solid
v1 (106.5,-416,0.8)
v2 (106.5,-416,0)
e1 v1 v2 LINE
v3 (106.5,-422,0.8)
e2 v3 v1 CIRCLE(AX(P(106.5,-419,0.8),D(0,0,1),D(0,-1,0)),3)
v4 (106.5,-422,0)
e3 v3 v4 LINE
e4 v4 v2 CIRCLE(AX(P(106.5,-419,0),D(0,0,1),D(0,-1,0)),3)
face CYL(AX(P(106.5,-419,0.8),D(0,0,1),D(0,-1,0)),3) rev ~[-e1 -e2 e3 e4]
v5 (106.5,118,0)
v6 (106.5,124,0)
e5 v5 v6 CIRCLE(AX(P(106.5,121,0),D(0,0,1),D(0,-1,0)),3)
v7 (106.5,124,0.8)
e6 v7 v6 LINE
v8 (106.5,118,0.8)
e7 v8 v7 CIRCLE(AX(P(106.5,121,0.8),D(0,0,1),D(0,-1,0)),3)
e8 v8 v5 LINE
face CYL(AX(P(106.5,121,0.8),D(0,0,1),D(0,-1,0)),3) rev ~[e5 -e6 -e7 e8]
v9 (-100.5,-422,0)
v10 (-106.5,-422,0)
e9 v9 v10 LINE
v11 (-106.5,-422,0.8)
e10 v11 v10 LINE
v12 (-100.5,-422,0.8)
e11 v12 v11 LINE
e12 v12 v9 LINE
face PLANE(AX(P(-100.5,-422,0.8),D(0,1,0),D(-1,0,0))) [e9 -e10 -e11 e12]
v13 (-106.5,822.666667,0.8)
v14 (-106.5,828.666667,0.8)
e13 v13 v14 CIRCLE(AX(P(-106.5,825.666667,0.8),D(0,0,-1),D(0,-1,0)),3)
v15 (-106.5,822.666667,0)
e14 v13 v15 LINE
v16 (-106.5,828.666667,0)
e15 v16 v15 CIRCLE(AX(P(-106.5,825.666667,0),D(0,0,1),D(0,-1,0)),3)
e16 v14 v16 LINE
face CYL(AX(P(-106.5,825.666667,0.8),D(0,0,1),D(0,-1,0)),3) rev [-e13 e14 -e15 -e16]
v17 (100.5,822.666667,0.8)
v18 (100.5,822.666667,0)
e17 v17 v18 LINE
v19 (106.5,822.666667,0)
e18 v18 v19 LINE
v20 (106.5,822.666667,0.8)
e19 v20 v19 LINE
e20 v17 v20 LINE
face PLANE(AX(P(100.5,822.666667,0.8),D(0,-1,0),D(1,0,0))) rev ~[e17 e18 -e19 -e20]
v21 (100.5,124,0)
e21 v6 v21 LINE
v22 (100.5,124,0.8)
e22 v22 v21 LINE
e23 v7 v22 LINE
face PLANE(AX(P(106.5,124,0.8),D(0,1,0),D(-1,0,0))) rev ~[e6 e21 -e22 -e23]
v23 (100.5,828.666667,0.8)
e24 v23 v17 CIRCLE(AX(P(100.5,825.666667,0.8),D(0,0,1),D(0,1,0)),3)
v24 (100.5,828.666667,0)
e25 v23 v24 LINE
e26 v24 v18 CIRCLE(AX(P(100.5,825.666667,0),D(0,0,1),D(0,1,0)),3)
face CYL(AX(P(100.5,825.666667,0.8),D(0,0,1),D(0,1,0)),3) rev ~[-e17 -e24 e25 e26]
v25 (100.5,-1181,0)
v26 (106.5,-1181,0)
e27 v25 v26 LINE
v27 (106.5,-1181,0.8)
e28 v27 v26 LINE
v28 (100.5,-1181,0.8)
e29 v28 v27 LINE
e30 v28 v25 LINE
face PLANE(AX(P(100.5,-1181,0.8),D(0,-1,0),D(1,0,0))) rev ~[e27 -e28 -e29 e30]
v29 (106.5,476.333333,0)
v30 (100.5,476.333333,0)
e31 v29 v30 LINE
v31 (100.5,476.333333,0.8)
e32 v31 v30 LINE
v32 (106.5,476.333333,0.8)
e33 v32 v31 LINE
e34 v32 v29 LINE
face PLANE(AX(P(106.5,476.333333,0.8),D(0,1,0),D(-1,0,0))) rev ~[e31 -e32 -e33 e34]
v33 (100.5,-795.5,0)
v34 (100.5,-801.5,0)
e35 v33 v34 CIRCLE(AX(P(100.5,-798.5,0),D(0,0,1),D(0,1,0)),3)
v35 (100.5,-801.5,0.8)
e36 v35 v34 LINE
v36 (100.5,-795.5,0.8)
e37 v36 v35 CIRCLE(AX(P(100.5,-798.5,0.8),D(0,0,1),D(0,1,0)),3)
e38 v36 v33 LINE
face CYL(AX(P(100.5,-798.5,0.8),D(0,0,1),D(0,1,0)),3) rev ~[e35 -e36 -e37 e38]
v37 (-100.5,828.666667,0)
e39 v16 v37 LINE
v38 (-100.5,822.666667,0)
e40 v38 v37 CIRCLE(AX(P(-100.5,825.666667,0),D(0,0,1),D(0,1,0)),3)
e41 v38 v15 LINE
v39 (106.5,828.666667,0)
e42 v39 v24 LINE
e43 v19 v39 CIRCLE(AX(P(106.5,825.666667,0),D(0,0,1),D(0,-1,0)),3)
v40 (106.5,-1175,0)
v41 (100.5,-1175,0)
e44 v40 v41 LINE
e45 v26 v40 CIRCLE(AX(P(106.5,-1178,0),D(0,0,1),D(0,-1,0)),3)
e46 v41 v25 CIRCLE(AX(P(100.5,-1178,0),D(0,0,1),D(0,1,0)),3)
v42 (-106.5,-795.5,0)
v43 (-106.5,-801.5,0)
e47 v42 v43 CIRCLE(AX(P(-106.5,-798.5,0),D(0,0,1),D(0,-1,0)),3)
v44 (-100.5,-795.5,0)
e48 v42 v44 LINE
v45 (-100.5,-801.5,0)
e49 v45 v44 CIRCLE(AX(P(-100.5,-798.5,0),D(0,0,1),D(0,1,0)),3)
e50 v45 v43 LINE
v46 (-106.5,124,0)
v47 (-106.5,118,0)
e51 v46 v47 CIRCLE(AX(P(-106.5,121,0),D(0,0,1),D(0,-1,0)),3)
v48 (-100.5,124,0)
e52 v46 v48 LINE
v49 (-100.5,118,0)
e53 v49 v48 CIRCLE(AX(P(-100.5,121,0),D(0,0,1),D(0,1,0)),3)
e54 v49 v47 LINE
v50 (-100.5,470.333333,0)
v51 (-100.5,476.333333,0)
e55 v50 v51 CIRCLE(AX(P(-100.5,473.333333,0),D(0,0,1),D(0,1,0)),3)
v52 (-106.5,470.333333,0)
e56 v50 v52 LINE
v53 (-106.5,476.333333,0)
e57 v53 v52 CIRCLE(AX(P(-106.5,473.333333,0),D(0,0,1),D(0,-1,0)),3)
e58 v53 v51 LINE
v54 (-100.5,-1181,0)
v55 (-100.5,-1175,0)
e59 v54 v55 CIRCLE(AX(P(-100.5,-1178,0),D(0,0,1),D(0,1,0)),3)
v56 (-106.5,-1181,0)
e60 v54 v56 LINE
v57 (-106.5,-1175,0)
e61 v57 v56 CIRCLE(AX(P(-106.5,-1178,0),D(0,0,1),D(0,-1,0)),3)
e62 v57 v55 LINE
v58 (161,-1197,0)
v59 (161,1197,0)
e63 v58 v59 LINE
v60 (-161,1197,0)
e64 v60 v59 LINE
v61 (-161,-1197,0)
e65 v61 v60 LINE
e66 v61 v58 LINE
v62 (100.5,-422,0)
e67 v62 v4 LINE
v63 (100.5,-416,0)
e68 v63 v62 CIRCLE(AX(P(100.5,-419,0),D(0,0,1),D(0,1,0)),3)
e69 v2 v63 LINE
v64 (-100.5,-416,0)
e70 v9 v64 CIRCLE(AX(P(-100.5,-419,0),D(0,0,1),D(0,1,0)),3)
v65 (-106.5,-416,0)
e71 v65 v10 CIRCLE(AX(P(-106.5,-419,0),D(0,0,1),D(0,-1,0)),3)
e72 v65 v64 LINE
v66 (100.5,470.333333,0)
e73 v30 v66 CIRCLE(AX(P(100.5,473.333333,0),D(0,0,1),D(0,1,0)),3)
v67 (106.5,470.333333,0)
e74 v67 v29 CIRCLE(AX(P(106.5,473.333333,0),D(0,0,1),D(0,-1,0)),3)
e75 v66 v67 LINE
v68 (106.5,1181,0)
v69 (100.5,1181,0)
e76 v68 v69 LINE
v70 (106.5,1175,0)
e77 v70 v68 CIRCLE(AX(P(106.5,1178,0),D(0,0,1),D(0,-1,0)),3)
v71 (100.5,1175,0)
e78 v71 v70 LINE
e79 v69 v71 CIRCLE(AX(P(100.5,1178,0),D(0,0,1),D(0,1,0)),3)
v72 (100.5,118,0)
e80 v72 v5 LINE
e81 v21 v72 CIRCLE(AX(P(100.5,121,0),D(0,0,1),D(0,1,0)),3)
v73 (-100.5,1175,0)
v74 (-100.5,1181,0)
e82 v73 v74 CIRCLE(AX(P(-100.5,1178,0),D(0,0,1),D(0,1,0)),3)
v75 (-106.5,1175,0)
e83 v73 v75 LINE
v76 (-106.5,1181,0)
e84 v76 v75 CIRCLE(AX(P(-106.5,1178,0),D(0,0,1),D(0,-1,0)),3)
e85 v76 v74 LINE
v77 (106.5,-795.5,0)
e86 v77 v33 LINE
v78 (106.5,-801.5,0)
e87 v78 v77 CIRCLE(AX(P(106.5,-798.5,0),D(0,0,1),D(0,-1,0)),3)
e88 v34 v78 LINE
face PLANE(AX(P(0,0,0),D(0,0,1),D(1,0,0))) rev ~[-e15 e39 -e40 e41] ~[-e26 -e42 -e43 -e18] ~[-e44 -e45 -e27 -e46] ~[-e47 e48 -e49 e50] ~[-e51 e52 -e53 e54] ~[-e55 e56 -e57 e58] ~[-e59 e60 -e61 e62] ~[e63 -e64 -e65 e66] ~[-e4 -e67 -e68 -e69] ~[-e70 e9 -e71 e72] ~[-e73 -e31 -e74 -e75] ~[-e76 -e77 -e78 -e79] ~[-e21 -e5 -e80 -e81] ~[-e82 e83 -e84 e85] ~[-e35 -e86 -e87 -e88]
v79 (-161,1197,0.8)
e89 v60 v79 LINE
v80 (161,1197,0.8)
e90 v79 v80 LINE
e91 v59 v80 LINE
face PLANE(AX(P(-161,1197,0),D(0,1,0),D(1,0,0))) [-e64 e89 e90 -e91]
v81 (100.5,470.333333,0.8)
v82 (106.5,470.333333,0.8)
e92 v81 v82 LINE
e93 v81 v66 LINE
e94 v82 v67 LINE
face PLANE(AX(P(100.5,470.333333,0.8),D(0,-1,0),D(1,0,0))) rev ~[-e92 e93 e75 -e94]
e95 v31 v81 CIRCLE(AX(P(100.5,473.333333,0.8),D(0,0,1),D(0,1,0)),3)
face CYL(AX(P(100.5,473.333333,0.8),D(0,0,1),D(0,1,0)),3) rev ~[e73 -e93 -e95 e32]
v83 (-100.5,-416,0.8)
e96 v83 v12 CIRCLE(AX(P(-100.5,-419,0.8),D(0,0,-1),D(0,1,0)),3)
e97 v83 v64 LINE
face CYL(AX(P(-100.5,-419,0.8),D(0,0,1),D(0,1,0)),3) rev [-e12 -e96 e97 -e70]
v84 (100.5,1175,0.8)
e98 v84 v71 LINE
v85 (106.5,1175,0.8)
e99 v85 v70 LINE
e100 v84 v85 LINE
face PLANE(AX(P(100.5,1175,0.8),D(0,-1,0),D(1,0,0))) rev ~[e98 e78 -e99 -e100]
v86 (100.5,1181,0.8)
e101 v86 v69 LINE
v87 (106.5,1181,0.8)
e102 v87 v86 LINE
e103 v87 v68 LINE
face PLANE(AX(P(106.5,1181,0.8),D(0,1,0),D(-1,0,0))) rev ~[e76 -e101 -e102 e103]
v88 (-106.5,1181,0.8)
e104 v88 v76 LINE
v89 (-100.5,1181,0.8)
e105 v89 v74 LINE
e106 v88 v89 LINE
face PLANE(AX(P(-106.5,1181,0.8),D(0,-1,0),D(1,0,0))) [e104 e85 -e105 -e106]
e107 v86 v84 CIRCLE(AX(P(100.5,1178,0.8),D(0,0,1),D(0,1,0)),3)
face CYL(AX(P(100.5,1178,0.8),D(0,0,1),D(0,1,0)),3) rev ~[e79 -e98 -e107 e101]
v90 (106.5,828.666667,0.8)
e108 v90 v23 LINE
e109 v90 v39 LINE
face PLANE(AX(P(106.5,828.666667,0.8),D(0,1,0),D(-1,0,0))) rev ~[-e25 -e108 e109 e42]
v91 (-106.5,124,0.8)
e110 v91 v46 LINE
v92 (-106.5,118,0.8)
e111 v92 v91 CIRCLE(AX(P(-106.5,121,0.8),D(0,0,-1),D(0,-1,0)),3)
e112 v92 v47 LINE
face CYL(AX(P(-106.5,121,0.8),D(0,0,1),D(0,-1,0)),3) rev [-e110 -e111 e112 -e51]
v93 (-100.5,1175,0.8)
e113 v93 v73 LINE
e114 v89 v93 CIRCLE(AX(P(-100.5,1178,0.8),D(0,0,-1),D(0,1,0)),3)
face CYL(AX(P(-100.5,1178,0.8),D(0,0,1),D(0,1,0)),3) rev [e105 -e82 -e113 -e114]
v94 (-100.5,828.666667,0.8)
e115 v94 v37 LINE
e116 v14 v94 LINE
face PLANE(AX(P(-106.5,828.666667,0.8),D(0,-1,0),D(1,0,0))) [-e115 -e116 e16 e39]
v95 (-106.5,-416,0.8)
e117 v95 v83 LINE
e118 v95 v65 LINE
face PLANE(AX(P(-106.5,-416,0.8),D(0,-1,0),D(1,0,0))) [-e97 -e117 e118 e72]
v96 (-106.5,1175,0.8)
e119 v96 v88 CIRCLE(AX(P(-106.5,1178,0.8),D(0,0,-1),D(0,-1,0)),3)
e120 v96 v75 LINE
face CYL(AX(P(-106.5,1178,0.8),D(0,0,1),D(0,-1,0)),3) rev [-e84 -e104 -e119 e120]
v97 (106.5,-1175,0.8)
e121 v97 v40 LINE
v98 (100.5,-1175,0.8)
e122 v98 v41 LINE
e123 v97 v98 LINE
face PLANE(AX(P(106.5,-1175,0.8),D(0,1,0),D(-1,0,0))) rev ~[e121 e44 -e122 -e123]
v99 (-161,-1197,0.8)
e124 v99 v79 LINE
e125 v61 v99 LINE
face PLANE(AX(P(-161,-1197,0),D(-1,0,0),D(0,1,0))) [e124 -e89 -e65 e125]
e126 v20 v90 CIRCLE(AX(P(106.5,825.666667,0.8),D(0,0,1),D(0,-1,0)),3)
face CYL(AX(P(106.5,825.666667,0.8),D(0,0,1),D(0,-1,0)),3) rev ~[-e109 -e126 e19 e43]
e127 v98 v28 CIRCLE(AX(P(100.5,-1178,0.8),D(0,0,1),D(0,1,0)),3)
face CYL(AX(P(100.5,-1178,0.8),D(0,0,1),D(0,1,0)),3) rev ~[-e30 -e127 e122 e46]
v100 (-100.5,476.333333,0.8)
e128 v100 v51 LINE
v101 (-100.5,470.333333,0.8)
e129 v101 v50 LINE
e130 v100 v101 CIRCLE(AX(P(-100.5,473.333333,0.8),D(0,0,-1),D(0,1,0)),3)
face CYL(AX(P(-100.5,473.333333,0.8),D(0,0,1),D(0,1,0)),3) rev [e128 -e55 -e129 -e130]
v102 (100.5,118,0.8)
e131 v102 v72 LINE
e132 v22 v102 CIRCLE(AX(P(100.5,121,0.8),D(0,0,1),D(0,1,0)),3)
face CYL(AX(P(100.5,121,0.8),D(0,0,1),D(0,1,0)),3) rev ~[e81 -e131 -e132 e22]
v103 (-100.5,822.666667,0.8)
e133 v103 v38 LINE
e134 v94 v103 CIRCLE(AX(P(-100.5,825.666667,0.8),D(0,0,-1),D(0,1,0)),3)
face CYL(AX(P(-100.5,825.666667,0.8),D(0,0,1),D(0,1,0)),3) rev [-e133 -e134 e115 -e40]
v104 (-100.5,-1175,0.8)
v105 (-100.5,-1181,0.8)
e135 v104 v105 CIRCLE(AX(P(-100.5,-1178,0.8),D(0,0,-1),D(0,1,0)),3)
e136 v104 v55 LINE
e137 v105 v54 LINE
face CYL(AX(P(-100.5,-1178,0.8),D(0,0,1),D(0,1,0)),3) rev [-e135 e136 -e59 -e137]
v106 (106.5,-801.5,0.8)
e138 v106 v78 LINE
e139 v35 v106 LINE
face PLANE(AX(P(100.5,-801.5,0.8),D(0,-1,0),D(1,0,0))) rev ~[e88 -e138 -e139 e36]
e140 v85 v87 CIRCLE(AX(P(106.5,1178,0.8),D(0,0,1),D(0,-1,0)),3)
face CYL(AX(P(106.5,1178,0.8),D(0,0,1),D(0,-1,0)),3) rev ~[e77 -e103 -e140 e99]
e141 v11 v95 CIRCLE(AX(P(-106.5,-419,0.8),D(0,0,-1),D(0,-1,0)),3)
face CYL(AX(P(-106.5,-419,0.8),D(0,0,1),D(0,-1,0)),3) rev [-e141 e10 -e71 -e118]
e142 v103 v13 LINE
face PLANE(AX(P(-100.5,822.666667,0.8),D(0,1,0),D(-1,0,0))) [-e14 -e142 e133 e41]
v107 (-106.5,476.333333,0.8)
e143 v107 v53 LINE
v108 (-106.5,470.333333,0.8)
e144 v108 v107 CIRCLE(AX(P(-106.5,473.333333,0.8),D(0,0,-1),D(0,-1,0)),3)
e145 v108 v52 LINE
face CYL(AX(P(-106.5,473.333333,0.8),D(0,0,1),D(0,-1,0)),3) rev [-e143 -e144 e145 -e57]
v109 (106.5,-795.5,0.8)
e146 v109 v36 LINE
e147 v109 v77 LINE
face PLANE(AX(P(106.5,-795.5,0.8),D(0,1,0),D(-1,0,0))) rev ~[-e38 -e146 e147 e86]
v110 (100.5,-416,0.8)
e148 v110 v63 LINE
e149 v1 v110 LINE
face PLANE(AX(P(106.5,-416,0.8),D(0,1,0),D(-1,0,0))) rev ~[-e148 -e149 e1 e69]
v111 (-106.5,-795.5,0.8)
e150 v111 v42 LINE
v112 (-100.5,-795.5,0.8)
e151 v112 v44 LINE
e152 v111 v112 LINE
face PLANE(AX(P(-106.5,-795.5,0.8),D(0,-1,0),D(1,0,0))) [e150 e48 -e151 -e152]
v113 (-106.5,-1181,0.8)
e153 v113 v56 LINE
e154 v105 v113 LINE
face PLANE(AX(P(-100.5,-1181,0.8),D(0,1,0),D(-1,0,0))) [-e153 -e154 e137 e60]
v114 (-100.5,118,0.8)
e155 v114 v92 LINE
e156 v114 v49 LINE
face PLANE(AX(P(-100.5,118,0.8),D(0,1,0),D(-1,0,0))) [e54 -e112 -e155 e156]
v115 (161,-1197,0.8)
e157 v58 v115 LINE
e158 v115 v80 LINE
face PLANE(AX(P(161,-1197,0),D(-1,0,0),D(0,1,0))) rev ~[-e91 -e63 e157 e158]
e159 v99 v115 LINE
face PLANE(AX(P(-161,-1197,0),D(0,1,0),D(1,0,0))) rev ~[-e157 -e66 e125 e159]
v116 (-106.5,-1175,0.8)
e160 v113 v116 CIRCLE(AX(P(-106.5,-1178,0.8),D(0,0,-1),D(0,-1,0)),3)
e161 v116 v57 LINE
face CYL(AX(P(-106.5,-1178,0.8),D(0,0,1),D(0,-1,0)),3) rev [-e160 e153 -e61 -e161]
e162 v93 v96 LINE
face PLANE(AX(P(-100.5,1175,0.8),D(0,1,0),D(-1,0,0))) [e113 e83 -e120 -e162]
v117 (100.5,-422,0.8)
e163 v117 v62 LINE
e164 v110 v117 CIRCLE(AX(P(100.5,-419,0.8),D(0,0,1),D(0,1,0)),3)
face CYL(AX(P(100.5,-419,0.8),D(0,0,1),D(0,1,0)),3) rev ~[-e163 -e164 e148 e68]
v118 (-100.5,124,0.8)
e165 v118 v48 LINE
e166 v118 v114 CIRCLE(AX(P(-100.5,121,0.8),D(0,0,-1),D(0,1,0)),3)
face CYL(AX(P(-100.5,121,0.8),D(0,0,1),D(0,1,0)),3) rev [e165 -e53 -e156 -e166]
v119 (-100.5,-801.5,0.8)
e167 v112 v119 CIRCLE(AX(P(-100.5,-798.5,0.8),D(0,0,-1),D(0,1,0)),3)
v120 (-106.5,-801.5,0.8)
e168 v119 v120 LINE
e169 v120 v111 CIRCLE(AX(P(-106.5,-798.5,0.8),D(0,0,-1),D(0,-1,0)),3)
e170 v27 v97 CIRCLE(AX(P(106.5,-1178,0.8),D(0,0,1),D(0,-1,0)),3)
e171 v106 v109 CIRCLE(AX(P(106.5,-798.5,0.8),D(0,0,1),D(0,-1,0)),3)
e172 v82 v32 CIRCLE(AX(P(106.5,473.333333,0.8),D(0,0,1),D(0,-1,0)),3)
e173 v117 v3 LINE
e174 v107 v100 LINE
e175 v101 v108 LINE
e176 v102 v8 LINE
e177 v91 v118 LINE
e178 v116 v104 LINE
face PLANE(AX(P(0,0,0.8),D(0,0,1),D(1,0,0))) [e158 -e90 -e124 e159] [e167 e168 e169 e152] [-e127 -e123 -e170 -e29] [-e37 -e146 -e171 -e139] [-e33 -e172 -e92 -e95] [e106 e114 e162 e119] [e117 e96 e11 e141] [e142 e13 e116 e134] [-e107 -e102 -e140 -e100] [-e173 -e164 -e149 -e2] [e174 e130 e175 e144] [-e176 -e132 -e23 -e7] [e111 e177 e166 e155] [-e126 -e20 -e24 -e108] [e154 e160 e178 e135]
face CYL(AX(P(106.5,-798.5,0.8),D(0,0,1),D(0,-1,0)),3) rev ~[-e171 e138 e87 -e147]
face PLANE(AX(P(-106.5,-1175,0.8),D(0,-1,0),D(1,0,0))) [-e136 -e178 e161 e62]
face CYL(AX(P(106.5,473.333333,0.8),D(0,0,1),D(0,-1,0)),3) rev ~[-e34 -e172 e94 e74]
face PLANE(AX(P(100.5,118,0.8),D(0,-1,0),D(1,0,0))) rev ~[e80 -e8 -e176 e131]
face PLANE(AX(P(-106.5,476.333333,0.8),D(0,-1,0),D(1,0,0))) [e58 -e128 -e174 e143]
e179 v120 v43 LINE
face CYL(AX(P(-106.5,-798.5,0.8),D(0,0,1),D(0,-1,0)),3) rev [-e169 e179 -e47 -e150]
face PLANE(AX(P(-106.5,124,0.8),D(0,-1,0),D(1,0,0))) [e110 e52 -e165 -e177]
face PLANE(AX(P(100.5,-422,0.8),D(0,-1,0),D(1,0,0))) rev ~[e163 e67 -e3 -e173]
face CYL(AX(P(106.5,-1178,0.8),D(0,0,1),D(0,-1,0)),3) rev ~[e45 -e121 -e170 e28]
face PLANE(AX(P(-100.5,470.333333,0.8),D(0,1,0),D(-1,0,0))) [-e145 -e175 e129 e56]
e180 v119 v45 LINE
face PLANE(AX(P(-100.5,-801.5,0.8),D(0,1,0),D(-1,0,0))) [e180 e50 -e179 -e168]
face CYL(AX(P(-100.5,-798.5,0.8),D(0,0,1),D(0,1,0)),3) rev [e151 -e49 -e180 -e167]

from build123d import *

# Parameters (mm, degrees)
SKETCH_1_W             = 322
SKETCH_1_H             = 2394
EXTRUDE_1_DEPTH        = 0.8
CUT_EXTRUDE_3001_DEPTH = 10


with BuildPart() as part:
    # 草图1 → 凸台-拉伸1 (new body)
    with BuildSketch(Plane.XY):
        Rectangle(SKETCH_1_W, SKETCH_1_H)
    extrude(amount=EXTRUDE_1_DEPTH)

    # 草图2 → 3001 (cut)
    with BuildSketch(Plane.XY.offset(0.8)):
        with BuildLine():
            Line((-106.5, 124), (-100.5, 124))
            ThreePointArc((-100.5, 124), (-97.5, 121), (-100.5, 118))
            Line((-100.5, 118), (-106.5, 118))
            ThreePointArc((-106.5, 118), (-109.5, 121), (-106.5, 124))
        make_face()
        with BuildLine():
            Line((-106.5, 1181), (-100.5, 1181))
            ThreePointArc((-100.5, 1181), (-97.5, 1178), (-100.5, 1175))
            Line((-100.5, 1175), (-106.5, 1175))
            ThreePointArc((-106.5, 1175), (-109.5, 1178), (-106.5, 1181))
        make_face()
        with BuildLine():
            Line((-106.5, 828.666666667), (-100.5, 828.666666667))
            ThreePointArc((-100.5, 828.666666667), (-97.5, 825.666666667), (-100.5, 822.666666667))
            Line((-100.5, 822.666666667), (-106.5, 822.666666667))
            ThreePointArc((-106.5, 822.666666667), (-109.5, 825.666666667), (-106.5, 828.666666667))
        make_face()
        with BuildLine():
            Line((-106.5, -1175), (-100.5, -1175))
            ThreePointArc((-100.5, -1175), (-97.5, -1178), (-100.5, -1181))
            Line((-100.5, -1181), (-106.5, -1181))
            ThreePointArc((-106.5, -1181), (-109.5, -1178), (-106.5, -1175))
        make_face()
        with BuildLine():
            Line((-106.5, 476.333333333), (-100.5, 476.333333333))
            ThreePointArc((-100.5, 476.333333333), (-97.5, 473.333333333), (-100.5, 470.333333333))
            Line((-100.5, 470.333333333), (-106.5, 470.333333333))
            ThreePointArc((-106.5, 470.333333333), (-109.5, 473.333333333), (-106.5, 476.333333333))
        make_face()
        with BuildLine():
            Line((-106.5, -795.5), (-100.5, -795.5))
            ThreePointArc((-100.5, -795.5), (-97.5, -798.5), (-100.5, -801.5))
            Line((-100.5, -801.5), (-106.5, -801.5))
            ThreePointArc((-106.5, -801.5), (-109.5, -798.5), (-106.5, -795.5))
        make_face()
        with BuildLine():
            Line((-106.5, -416), (-100.5, -416))
            ThreePointArc((-100.5, -416), (-97.5, -419), (-100.5, -422))
            Line((-100.5, -422), (-106.5, -422))
            ThreePointArc((-106.5, -422), (-109.5, -419), (-106.5, -416))
        make_face()
        with BuildLine():
            Line((106.5, -1175), (100.5, -1175))
            ThreePointArc((100.5, -1175), (97.5, -1178), (100.5, -1181))
            Line((100.5, -1181), (106.5, -1181))
            ThreePointArc((106.5, -1181), (109.5, -1178), (106.5, -1175))
        make_face()
        with BuildLine():
            Line((106.5, -795.5), (100.5, -795.5))
            ThreePointArc((100.5, -795.5), (97.5, -798.5), (100.5, -801.5))
            Line((100.5, -801.5), (106.5, -801.5))
            ThreePointArc((106.5, -801.5), (109.5, -798.5), (106.5, -795.5))
        make_face()
        with BuildLine():
            Line((106.5, -416), (100.5, -416))
            ThreePointArc((100.5, -416), (97.5, -419), (100.5, -422))
            Line((100.5, -422), (106.5, -422))
            ThreePointArc((106.5, -422), (109.5, -419), (106.5, -416))
        make_face()
        with BuildLine():
            Line((106.5, 476.333333333), (100.5, 476.333333333))
            ThreePointArc((100.5, 476.333333333), (97.5, 473.333333333), (100.5, 470.333333333))
            Line((100.5, 470.333333333), (106.5, 470.333333333))
            ThreePointArc((106.5, 470.333333333), (109.5, 473.333333333), (106.5, 476.333333333))
        make_face()
        with BuildLine():
            Line((106.5, 828.666666667), (100.5, 828.666666667))
            ThreePointArc((100.5, 828.666666667), (97.5, 825.666666667), (100.5, 822.666666667))
            Line((100.5, 822.666666667), (106.5, 822.666666667))
            ThreePointArc((106.5, 822.666666667), (109.5, 825.666666667), (106.5, 828.666666667))
        make_face()
        with BuildLine():
            Line((106.5, 1181), (100.5, 1181))
            ThreePointArc((100.5, 1181), (97.5, 1178), (100.5, 1175))
            Line((100.5, 1175), (106.5, 1175))
            ThreePointArc((106.5, 1175), (109.5, 1178), (106.5, 1181))
        make_face()
        with BuildLine():
            Line((106.5, 124), (100.5, 124))
            ThreePointArc((100.5, 124), (97.5, 121), (100.5, 118))
            Line((100.5, 118), (106.5, 118))
            ThreePointArc((106.5, 118), (109.5, 121), (106.5, 124))
        make_face()
    extrude(amount=-CUT_EXTRUDE_3001_DEPTH, mode=Mode.SUBTRACT)


solid = part.part
